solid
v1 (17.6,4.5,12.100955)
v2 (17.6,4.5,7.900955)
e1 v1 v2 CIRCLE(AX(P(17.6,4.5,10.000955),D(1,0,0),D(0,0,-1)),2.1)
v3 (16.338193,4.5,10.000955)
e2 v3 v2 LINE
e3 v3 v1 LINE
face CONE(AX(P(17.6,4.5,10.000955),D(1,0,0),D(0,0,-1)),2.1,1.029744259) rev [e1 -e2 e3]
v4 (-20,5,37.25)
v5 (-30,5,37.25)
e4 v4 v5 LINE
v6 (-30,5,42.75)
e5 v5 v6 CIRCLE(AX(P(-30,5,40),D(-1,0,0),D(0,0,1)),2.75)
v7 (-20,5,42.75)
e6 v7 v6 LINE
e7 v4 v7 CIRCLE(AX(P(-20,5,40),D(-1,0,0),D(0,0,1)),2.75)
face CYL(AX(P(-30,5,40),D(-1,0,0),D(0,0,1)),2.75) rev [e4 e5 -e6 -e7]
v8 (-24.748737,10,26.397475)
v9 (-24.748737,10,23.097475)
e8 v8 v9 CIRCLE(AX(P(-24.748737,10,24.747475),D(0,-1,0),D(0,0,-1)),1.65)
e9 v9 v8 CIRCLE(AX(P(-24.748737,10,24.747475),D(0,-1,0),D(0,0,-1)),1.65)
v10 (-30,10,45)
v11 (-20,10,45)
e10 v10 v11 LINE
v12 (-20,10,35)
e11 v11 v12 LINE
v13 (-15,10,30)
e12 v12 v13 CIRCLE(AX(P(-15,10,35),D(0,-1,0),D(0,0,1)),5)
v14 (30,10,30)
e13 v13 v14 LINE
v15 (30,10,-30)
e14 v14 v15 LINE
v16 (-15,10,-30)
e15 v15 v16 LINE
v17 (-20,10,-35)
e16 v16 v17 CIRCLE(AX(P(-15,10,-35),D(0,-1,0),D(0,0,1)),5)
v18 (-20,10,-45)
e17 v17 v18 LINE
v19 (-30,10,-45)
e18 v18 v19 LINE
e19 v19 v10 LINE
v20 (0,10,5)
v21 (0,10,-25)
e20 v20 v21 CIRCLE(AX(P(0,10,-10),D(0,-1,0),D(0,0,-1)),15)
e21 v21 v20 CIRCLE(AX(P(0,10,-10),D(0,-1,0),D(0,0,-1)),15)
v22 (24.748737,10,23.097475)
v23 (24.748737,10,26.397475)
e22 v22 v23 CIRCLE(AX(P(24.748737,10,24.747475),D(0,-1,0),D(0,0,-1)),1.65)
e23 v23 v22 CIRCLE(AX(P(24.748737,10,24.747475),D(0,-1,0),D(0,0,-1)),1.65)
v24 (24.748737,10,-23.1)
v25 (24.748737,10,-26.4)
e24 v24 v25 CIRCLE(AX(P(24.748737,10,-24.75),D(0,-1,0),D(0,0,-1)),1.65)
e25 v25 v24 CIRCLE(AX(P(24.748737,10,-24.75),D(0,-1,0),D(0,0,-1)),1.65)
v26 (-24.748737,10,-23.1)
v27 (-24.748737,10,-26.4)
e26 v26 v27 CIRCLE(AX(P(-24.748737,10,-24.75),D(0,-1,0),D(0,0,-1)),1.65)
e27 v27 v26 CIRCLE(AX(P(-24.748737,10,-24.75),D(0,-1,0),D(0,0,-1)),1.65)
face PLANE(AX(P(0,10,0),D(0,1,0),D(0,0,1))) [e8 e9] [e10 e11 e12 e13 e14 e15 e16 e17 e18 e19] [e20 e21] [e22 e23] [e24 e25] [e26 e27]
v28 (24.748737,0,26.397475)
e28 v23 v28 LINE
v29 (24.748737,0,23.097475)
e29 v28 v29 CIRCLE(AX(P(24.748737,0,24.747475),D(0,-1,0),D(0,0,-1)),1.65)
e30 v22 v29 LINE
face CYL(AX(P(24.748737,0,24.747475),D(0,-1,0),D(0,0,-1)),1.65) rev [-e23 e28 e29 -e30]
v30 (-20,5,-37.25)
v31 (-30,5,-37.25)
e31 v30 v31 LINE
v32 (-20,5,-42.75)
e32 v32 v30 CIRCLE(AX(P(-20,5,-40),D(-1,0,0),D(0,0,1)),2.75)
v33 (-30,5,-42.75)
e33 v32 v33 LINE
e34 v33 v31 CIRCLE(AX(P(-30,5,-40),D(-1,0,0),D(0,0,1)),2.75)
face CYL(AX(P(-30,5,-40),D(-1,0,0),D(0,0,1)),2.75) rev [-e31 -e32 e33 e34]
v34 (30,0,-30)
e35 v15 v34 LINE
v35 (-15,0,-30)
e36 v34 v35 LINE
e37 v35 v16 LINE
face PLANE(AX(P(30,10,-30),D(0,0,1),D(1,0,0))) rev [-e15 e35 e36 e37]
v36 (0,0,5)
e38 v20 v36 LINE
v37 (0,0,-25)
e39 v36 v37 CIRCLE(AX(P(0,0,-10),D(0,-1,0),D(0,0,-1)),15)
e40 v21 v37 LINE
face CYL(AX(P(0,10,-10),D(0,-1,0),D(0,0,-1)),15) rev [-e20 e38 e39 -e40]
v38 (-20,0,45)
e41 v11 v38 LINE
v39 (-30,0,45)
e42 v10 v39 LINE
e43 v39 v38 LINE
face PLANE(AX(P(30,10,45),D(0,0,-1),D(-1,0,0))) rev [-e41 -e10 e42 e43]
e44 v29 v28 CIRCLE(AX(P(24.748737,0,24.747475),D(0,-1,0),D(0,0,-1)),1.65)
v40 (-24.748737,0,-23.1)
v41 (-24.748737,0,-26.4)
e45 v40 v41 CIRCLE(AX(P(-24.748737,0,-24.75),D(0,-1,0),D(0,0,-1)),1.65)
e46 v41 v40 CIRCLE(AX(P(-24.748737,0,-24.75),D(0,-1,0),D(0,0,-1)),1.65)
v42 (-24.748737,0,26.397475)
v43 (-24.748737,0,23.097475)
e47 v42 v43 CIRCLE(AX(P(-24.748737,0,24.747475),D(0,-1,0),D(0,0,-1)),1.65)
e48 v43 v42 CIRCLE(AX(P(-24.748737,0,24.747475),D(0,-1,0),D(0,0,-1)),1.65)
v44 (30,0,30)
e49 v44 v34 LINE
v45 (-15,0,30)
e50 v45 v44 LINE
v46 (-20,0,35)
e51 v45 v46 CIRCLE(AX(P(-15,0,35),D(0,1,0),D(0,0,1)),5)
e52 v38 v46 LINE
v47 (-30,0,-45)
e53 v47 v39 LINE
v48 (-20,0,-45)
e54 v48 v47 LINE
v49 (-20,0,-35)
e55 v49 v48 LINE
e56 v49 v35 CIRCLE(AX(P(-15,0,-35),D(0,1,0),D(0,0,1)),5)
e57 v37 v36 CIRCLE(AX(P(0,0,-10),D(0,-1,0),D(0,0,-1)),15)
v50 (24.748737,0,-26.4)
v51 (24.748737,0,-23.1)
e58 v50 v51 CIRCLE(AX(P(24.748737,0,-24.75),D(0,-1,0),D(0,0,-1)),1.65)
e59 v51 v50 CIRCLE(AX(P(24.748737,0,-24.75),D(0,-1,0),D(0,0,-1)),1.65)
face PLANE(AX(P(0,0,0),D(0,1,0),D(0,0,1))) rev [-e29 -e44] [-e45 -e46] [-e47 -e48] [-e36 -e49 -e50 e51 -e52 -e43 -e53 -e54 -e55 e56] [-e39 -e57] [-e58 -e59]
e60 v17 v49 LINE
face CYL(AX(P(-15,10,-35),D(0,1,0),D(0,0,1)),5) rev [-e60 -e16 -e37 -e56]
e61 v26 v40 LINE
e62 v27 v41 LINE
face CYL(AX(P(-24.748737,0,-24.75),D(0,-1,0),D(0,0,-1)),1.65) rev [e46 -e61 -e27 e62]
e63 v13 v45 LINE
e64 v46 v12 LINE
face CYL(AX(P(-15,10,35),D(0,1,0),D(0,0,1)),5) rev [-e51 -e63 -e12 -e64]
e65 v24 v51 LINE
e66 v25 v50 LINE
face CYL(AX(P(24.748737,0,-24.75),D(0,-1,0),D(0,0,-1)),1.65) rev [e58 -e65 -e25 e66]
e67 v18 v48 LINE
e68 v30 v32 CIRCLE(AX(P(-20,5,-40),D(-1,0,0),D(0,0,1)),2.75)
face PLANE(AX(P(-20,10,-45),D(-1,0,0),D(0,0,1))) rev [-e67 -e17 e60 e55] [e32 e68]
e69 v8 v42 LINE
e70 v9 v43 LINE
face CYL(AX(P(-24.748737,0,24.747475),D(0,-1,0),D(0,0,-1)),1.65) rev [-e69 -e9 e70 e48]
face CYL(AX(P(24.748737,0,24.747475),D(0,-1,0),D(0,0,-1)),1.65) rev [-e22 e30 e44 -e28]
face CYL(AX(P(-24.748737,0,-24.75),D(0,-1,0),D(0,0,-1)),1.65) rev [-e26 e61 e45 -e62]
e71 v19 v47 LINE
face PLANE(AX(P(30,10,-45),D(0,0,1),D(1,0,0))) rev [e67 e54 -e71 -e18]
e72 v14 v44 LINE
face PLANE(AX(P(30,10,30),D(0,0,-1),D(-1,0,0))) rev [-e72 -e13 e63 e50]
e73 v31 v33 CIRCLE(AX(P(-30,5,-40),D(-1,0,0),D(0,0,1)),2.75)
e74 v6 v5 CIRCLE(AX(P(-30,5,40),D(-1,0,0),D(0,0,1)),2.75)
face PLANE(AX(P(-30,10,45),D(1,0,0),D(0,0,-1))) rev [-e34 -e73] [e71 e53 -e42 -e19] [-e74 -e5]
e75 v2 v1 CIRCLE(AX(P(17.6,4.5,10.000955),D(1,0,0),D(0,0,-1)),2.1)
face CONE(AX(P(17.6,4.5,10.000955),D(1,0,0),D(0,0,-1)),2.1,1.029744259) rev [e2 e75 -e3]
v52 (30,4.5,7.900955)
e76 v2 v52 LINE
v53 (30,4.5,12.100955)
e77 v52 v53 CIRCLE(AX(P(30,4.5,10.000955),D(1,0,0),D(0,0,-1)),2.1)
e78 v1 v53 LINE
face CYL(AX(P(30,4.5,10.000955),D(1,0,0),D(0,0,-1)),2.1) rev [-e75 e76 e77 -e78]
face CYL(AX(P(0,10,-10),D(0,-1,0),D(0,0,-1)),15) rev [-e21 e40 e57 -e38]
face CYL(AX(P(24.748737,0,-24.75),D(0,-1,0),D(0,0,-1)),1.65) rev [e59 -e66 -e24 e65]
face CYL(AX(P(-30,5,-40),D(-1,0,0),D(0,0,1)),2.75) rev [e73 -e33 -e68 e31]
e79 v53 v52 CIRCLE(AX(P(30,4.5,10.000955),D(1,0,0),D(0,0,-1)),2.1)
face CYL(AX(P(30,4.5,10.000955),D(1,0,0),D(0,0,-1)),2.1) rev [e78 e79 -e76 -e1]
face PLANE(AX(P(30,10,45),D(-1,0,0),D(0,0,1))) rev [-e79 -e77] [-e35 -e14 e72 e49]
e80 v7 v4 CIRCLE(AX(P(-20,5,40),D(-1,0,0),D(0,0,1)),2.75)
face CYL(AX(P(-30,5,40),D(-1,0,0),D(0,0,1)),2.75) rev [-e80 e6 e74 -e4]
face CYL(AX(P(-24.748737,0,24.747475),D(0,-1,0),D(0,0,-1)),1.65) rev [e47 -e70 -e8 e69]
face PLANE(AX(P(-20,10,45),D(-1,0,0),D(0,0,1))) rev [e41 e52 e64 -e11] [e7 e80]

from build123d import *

# Parameters (mm, degrees)
SKETCH1_W                      = 60
SKETCH1_H                      = 90
BOSS_EXTRUDE1_DEPTH            = 10
SKETCH4_R                      = 15
CUT_EXTRUDE3_DEPTH             = 56
M4_TAPPED_HOLE1_D              = 3.3
SKETCH8_W                      = 50
SKETCH8_H                      = 15
CUT_EXTRUDE5_DEPTH             = 56
F_5_5_5_5_DIAMETER_HOLE1_D     = 5.5
F_5_5_5_5_DIAMETER_HOLE1_DEPTH = 12.4
F_5_5_5_5_DIAMETER_HOLE1_TIP   = 1.652366702
FILLET1_R                      = 5
M5_TAPPED_HOLE1_D              = 4.2
M5_TAPPED_HOLE1_DEPTH          = 12.4
M5_TAPPED_HOLE1_TIP            = 1.2618073


with BuildPart() as part:
    # Sketch1 → Boss-Extrude1 (new body)
    with BuildSketch(Plane(origin=(0, 0, 0), x_dir=(1, 0, 0), z_dir=(0, 1, 0))):
        Rectangle(SKETCH1_W, SKETCH1_H)
    extrude(amount=BOSS_EXTRUDE1_DEPTH)

    # Sketch4 → Cut-Extrude3 (cut, through all)
    with BuildSketch(Plane.XZ):
        with Locations(Location((0, -10, 0), (0, 0, 270))):
            Circle(SKETCH4_R)
    extrude(amount=-CUT_EXTRUDE3_DEPTH, mode=Mode.SUBTRACT)

    # M4 Tapped Hole1 (through all)
    with Locations(Plane.XZ):
        with Locations((-24.748737342, 24.747474683), (-24.748737342, -24.75), (24.748737342, -24.75), (24.748737342, 24.747474683)):
            Hole(M4_TAPPED_HOLE1_D / 2)

    # Sketch8 → Cut-Extrude5 (cut, through all)
    with BuildSketch(Plane.XZ):
        with Locations((5, 37.5)):
            Rectangle(SKETCH8_W, SKETCH8_H)
        with Locations((5, -37.5)):
            Rectangle(SKETCH8_W, SKETCH8_H)
    extrude(amount=-CUT_EXTRUDE5_DEPTH, mode=Mode.SUBTRACT)

    # Ø5.5 (5.5) Diameter Hole1
    with Locations(Plane.ZY.offset(30)):
        with Locations((-40, 5), (40, 5)):
            Hole(F_5_5_5_5_DIAMETER_HOLE1_D / 2, depth=F_5_5_5_5_DIAMETER_HOLE1_DEPTH)
            with Locations((0, 0, -(F_5_5_5_5_DIAMETER_HOLE1_DEPTH + F_5_5_5_5_DIAMETER_HOLE1_TIP / 2))):  # 118° drill point
                Cone(0, F_5_5_5_5_DIAMETER_HOLE1_D / 2, F_5_5_5_5_DIAMETER_HOLE1_TIP, mode=Mode.SUBTRACT)

    # Fillet1
    fillet1_edges = [part.edges().sort_by_distance(p)[0] for p in [
        (-20, 5, 30),
        (-20, 5, -30),
    ]]
    fillet(fillet1_edges, radius=FILLET1_R)

    # M5 Tapped Hole1
    with Locations(Plane(origin=(30, 0, 0), x_dir=(0, 0, -1), z_dir=(1, 0, 0))):
        with Locations((-10.000955133, 4.5)):
            Hole(M5_TAPPED_HOLE1_D / 2, depth=M5_TAPPED_HOLE1_DEPTH)
            with Locations((0, 0, -(M5_TAPPED_HOLE1_DEPTH + M5_TAPPED_HOLE1_TIP / 2))):  # 118° drill point
                Cone(0, M5_TAPPED_HOLE1_D / 2, M5_TAPPED_HOLE1_TIP, mode=Mode.SUBTRACT)


solid = part.part
